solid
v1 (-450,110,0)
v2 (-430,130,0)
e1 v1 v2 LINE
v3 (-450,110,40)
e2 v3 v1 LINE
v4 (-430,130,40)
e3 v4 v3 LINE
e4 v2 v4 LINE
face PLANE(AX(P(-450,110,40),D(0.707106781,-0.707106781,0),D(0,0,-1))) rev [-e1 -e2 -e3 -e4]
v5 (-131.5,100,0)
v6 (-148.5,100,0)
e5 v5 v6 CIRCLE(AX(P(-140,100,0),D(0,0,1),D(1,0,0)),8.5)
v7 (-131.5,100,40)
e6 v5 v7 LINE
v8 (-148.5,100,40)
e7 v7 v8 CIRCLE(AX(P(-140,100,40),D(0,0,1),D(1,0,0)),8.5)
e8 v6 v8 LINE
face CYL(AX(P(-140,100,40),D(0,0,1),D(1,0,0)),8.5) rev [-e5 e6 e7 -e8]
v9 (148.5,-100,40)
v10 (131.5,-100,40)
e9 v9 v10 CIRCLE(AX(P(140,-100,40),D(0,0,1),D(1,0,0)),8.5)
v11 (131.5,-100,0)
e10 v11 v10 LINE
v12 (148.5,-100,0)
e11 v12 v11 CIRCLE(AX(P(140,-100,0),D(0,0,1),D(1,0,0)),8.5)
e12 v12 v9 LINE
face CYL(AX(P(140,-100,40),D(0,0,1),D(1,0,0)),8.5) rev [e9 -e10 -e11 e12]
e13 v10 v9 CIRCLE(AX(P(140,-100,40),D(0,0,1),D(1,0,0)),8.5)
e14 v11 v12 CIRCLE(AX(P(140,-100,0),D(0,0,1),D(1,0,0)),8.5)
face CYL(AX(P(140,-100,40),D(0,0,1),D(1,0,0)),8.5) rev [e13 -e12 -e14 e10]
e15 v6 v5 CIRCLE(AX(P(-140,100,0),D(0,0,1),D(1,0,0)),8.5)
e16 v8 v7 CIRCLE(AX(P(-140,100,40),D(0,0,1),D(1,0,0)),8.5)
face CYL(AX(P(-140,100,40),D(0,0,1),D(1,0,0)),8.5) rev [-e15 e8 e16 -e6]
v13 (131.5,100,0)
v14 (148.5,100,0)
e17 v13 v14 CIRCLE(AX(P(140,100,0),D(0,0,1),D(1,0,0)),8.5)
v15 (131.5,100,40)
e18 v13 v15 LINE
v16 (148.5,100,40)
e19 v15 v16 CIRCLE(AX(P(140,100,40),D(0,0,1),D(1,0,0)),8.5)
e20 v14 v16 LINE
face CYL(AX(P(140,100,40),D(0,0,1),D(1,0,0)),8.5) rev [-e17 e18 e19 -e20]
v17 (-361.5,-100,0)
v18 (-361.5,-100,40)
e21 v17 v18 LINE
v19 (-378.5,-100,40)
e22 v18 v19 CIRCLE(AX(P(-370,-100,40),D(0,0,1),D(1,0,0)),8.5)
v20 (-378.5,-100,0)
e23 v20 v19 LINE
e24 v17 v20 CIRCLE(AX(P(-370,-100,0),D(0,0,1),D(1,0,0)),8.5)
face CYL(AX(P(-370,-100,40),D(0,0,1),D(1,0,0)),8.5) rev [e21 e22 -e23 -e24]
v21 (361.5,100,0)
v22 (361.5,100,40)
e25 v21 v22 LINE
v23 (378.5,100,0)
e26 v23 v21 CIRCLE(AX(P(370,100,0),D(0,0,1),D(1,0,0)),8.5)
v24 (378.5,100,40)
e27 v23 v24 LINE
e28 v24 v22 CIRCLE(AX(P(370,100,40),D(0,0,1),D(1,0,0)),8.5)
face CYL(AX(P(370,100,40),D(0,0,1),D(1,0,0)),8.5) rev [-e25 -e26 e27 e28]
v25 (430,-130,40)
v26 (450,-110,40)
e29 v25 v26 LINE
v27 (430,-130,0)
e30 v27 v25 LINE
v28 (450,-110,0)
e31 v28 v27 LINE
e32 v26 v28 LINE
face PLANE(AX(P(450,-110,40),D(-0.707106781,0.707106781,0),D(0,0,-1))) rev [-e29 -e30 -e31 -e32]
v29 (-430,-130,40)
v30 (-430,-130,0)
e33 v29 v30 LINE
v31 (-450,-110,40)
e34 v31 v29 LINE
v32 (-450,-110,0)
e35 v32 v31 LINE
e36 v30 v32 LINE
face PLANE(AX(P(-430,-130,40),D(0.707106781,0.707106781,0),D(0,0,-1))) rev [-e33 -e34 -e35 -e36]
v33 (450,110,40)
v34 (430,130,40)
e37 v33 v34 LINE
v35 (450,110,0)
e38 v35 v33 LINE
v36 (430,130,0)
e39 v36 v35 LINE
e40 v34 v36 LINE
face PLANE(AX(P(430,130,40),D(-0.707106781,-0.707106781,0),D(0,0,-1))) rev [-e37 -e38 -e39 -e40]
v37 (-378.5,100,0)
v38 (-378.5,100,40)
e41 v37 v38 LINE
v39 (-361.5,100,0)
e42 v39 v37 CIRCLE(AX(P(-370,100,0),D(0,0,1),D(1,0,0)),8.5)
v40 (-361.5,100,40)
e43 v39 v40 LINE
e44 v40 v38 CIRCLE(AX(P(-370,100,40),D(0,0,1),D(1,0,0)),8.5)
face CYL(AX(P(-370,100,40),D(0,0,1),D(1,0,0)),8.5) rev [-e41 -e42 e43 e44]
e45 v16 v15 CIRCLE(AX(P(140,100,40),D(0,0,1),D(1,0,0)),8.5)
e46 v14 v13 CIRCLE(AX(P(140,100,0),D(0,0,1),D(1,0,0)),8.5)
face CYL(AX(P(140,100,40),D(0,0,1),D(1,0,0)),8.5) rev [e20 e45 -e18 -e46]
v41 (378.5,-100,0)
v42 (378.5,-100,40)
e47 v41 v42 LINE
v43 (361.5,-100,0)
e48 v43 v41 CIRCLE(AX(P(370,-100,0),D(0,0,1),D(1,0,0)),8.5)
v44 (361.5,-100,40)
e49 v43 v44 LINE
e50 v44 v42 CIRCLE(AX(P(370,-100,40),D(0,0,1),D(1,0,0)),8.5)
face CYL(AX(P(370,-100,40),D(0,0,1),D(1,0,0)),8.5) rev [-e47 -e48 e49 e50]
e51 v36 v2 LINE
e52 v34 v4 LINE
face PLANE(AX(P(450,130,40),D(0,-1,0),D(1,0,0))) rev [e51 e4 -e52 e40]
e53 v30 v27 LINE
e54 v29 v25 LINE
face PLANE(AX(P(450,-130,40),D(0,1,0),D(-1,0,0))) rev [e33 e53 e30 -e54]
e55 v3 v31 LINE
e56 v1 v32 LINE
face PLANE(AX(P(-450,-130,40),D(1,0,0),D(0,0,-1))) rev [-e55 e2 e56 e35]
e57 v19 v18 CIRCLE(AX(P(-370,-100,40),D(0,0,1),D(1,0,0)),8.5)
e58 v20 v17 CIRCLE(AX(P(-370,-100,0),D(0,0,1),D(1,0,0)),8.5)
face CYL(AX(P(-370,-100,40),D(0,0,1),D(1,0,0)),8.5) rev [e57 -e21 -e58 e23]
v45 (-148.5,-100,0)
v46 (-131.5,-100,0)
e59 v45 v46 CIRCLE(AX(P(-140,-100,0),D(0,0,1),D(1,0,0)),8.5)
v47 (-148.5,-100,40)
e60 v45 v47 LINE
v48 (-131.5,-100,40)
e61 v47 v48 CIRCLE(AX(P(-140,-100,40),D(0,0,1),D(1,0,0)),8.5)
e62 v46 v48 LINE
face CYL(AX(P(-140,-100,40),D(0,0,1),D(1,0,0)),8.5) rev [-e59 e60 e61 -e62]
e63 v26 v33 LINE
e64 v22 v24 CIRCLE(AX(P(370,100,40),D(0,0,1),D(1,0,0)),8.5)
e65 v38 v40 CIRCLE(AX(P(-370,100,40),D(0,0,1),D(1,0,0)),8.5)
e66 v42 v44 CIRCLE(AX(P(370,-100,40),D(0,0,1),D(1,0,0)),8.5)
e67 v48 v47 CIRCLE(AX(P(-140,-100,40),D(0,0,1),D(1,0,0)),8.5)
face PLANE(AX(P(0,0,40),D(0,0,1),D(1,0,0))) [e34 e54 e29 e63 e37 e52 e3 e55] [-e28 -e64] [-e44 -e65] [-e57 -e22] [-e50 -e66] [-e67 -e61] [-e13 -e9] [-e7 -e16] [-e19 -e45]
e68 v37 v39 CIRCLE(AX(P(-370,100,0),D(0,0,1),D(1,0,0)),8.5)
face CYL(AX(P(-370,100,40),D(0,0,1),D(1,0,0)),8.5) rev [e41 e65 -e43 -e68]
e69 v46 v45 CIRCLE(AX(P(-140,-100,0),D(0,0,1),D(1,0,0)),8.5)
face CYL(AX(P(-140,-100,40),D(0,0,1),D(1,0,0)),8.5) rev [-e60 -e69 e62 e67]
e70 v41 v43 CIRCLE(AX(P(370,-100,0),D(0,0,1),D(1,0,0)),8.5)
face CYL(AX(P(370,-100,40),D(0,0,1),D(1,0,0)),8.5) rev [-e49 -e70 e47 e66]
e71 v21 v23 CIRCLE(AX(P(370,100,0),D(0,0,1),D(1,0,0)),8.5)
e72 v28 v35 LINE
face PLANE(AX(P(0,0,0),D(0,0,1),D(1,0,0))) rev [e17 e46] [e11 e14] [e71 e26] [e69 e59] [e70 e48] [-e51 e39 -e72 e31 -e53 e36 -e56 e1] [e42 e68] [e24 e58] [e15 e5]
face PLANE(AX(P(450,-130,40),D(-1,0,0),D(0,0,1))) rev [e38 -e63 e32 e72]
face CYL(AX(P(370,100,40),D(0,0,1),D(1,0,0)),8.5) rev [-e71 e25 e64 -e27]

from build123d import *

# Parameters (mm, degrees)
SKETCH1_W                      = 900
SKETCH1_H                      = 260
BOSS_EXTRUDE1_DEPTH            = 40
F_17_0_17_DIAMETER_HOLE1_D     = 17
F_17_0_17_DIAMETER_HOLE1_DEPTH = 42
F_17_0_17_DIAMETER_HOLE1_TIP   = 5.107315262
CHAMFER1_SIZE                  = 20


with BuildPart() as part:
    # Sketch1 → Boss-Extrude1 (new body)
    with BuildSketch(Plane.XY):
        Rectangle(SKETCH1_W, SKETCH1_H)
    extrude(amount=BOSS_EXTRUDE1_DEPTH)

    # Ø17.0 (17) Diameter Hole1
    with Locations(Plane.XY.offset(40)):
        with Locations((-370, 100), (-140, 100), (-370, -100), (-140, -100), (140, -100), (370, -100), (140, 100), (370, 100)):
            Hole(F_17_0_17_DIAMETER_HOLE1_D / 2, depth=F_17_0_17_DIAMETER_HOLE1_DEPTH)
            with Locations((0, 0, -(F_17_0_17_DIAMETER_HOLE1_DEPTH + F_17_0_17_DIAMETER_HOLE1_TIP / 2))):  # 118° drill point
                Cone(0, F_17_0_17_DIAMETER_HOLE1_D / 2, F_17_0_17_DIAMETER_HOLE1_TIP, mode=Mode.SUBTRACT)

    # Chamfer1
    chamfer1_edges = [part.edges().sort_by_distance(p)[0] for p in [
        (-450, 130, 20),
        (450, 130, 20),
        (450, -130, 20),
        (-450, -130, 20),
    ]]
    chamfer(chamfer1_edges, length=CHAMFER1_SIZE)


solid = part.part
